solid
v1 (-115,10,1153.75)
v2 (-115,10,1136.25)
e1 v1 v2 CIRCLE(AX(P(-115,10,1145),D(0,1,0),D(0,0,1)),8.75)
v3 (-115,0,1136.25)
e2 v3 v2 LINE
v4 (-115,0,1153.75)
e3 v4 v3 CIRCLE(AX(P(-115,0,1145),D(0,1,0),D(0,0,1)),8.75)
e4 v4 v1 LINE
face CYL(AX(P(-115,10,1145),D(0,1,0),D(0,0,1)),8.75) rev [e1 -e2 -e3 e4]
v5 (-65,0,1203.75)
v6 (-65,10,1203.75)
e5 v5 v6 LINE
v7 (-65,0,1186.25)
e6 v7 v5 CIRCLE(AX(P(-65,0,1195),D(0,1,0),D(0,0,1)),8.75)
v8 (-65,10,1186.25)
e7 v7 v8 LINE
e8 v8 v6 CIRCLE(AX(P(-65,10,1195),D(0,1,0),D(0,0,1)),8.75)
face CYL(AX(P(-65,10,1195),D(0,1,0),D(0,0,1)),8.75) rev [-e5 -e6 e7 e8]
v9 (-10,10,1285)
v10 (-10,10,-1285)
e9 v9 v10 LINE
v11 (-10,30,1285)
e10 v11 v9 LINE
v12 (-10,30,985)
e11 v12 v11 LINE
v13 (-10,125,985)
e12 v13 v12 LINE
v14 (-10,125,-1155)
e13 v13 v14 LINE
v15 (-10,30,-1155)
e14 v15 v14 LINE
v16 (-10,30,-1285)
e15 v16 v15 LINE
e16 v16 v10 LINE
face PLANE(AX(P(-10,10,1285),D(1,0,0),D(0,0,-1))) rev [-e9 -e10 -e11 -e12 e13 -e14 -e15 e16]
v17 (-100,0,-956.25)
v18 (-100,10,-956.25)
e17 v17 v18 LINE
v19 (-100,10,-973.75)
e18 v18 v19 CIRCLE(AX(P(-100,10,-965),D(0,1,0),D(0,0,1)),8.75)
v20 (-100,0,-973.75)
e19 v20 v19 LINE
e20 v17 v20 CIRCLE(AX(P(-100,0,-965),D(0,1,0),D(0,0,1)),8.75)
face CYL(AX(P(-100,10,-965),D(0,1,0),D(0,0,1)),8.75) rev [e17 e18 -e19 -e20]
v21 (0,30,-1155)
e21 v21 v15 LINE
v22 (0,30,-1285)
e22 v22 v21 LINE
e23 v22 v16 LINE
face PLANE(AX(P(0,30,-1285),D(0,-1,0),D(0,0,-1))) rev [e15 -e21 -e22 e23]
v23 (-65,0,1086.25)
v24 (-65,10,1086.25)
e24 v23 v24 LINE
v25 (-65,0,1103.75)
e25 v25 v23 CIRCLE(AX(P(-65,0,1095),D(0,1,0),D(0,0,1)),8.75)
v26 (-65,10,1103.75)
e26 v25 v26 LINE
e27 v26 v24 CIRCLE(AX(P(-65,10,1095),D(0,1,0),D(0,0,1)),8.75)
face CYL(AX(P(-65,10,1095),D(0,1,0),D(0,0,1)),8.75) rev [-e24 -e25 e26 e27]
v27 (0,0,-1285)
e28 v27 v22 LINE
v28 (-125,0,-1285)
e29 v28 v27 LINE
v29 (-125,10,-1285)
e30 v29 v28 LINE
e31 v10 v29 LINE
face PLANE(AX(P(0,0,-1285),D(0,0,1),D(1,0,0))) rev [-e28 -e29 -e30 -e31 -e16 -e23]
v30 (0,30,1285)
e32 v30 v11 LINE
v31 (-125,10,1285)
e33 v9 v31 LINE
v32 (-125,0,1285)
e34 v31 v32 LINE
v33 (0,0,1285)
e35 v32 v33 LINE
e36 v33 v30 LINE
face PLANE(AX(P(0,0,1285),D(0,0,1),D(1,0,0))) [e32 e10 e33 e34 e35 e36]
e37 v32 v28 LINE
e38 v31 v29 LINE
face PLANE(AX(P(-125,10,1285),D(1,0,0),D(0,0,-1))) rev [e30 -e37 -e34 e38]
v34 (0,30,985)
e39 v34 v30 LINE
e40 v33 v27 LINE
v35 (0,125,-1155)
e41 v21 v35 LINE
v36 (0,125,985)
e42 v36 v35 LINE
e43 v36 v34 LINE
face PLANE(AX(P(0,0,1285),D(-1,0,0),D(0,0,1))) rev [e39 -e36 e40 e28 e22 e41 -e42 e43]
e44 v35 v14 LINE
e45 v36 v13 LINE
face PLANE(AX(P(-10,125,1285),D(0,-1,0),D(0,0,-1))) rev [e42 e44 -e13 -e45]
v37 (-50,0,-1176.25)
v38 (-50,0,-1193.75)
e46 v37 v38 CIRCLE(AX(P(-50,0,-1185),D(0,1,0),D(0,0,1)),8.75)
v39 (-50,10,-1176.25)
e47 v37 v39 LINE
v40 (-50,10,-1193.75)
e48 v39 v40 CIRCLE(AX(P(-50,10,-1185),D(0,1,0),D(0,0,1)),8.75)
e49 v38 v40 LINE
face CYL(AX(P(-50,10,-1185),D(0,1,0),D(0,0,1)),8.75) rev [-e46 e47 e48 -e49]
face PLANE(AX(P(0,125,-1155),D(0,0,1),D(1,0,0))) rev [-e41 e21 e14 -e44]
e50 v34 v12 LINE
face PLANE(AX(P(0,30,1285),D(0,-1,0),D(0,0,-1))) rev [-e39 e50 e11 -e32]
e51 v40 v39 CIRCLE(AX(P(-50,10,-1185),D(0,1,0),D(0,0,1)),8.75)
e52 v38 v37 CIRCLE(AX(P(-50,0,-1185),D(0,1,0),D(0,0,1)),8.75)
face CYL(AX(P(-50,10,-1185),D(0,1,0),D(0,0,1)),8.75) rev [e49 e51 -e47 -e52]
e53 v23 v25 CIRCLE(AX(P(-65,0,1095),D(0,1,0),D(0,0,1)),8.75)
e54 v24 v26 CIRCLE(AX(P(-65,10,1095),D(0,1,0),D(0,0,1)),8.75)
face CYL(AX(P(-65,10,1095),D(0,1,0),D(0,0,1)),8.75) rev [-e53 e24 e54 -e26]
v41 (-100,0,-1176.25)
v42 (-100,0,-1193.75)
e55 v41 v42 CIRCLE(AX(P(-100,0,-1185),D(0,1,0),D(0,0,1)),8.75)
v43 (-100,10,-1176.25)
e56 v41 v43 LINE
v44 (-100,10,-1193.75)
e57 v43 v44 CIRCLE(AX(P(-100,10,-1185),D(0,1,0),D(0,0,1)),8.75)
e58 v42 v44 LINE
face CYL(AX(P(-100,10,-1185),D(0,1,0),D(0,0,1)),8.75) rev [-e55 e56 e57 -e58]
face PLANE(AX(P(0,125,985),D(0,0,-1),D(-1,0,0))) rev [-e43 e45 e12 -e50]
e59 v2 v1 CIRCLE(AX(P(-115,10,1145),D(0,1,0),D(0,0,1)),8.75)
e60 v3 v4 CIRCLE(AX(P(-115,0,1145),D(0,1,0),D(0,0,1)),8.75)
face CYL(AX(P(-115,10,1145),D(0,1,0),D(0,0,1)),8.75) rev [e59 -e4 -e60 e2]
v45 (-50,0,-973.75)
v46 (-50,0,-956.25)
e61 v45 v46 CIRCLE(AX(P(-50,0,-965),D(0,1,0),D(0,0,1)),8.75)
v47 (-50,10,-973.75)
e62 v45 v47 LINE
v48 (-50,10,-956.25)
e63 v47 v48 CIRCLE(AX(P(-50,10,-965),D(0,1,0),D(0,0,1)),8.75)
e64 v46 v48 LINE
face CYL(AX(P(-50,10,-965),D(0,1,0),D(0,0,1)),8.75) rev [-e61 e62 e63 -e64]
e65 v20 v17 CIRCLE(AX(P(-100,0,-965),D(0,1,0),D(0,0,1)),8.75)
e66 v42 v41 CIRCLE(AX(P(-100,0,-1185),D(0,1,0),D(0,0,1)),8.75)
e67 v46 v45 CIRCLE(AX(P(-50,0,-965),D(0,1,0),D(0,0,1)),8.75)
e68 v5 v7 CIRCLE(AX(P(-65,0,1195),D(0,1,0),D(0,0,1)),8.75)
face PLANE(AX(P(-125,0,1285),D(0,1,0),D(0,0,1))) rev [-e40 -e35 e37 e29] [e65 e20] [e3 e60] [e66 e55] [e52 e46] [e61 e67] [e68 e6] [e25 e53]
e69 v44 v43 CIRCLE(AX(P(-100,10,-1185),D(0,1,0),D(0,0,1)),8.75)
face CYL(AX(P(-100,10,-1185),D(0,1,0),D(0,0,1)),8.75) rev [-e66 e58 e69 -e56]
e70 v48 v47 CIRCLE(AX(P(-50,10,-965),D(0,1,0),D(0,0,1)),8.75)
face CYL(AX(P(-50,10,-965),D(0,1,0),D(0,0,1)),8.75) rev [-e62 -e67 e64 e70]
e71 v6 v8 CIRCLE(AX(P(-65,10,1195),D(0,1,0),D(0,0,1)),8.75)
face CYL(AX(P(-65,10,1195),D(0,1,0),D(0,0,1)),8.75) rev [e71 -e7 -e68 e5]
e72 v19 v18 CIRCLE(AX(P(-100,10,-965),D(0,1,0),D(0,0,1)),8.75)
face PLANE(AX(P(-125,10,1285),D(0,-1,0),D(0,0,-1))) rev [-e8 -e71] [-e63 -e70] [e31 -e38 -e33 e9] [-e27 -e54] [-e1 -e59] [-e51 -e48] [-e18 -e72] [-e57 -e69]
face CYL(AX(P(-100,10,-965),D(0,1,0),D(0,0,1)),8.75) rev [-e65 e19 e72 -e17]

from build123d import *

# Parameters (mm, degrees)
EXTRUDE_1_DEPTH     = 1285
HOLE_WIZARD_M20_1_D = 17.5
SKETCH_4_W          = 300
SKETCH_4_H          = 95
SKETCH_4_W_2        = 130
CUT_EXTRUDE_1_DEPTH = 1297.177071237


with BuildPart() as part:
    # 草图1 → 凸台-拉伸1 (new, symmetric)
    with BuildSketch(Plane.XY):
        Polygon((-125, 0), (0, 0), (0, 125), (-10, 125), (-10, 10), (-125, 10), align=None)
    extrude(amount=EXTRUDE_1_DEPTH, both=True)

    # M20 螺纹孔1 (through all)
    with Locations(Plane(origin=(0, 10, 0), x_dir=(1, 0, 0), z_dir=(0, 1, 0))):
        with Locations((-100, 965), (-50, 965), (-50, 1185), (-100, 1185), (-115, -1145), (-65, -1095), (-65, -1195)):
            Hole(HOLE_WIZARD_M20_1_D / 2)

    # 草图4 → 切除-拉伸1 (cut, through all)
    with BuildSketch(Plane.ZY.offset(10)):
        with Locations((1135, 77.5)):
            Rectangle(SKETCH_4_W, SKETCH_4_H)
        with Locations((-1220, 77.5)):
            Rectangle(SKETCH_4_W_2, SKETCH_4_H)
    extrude(amount=-CUT_EXTRUDE_1_DEPTH, mode=Mode.SUBTRACT)


solid = part.part
